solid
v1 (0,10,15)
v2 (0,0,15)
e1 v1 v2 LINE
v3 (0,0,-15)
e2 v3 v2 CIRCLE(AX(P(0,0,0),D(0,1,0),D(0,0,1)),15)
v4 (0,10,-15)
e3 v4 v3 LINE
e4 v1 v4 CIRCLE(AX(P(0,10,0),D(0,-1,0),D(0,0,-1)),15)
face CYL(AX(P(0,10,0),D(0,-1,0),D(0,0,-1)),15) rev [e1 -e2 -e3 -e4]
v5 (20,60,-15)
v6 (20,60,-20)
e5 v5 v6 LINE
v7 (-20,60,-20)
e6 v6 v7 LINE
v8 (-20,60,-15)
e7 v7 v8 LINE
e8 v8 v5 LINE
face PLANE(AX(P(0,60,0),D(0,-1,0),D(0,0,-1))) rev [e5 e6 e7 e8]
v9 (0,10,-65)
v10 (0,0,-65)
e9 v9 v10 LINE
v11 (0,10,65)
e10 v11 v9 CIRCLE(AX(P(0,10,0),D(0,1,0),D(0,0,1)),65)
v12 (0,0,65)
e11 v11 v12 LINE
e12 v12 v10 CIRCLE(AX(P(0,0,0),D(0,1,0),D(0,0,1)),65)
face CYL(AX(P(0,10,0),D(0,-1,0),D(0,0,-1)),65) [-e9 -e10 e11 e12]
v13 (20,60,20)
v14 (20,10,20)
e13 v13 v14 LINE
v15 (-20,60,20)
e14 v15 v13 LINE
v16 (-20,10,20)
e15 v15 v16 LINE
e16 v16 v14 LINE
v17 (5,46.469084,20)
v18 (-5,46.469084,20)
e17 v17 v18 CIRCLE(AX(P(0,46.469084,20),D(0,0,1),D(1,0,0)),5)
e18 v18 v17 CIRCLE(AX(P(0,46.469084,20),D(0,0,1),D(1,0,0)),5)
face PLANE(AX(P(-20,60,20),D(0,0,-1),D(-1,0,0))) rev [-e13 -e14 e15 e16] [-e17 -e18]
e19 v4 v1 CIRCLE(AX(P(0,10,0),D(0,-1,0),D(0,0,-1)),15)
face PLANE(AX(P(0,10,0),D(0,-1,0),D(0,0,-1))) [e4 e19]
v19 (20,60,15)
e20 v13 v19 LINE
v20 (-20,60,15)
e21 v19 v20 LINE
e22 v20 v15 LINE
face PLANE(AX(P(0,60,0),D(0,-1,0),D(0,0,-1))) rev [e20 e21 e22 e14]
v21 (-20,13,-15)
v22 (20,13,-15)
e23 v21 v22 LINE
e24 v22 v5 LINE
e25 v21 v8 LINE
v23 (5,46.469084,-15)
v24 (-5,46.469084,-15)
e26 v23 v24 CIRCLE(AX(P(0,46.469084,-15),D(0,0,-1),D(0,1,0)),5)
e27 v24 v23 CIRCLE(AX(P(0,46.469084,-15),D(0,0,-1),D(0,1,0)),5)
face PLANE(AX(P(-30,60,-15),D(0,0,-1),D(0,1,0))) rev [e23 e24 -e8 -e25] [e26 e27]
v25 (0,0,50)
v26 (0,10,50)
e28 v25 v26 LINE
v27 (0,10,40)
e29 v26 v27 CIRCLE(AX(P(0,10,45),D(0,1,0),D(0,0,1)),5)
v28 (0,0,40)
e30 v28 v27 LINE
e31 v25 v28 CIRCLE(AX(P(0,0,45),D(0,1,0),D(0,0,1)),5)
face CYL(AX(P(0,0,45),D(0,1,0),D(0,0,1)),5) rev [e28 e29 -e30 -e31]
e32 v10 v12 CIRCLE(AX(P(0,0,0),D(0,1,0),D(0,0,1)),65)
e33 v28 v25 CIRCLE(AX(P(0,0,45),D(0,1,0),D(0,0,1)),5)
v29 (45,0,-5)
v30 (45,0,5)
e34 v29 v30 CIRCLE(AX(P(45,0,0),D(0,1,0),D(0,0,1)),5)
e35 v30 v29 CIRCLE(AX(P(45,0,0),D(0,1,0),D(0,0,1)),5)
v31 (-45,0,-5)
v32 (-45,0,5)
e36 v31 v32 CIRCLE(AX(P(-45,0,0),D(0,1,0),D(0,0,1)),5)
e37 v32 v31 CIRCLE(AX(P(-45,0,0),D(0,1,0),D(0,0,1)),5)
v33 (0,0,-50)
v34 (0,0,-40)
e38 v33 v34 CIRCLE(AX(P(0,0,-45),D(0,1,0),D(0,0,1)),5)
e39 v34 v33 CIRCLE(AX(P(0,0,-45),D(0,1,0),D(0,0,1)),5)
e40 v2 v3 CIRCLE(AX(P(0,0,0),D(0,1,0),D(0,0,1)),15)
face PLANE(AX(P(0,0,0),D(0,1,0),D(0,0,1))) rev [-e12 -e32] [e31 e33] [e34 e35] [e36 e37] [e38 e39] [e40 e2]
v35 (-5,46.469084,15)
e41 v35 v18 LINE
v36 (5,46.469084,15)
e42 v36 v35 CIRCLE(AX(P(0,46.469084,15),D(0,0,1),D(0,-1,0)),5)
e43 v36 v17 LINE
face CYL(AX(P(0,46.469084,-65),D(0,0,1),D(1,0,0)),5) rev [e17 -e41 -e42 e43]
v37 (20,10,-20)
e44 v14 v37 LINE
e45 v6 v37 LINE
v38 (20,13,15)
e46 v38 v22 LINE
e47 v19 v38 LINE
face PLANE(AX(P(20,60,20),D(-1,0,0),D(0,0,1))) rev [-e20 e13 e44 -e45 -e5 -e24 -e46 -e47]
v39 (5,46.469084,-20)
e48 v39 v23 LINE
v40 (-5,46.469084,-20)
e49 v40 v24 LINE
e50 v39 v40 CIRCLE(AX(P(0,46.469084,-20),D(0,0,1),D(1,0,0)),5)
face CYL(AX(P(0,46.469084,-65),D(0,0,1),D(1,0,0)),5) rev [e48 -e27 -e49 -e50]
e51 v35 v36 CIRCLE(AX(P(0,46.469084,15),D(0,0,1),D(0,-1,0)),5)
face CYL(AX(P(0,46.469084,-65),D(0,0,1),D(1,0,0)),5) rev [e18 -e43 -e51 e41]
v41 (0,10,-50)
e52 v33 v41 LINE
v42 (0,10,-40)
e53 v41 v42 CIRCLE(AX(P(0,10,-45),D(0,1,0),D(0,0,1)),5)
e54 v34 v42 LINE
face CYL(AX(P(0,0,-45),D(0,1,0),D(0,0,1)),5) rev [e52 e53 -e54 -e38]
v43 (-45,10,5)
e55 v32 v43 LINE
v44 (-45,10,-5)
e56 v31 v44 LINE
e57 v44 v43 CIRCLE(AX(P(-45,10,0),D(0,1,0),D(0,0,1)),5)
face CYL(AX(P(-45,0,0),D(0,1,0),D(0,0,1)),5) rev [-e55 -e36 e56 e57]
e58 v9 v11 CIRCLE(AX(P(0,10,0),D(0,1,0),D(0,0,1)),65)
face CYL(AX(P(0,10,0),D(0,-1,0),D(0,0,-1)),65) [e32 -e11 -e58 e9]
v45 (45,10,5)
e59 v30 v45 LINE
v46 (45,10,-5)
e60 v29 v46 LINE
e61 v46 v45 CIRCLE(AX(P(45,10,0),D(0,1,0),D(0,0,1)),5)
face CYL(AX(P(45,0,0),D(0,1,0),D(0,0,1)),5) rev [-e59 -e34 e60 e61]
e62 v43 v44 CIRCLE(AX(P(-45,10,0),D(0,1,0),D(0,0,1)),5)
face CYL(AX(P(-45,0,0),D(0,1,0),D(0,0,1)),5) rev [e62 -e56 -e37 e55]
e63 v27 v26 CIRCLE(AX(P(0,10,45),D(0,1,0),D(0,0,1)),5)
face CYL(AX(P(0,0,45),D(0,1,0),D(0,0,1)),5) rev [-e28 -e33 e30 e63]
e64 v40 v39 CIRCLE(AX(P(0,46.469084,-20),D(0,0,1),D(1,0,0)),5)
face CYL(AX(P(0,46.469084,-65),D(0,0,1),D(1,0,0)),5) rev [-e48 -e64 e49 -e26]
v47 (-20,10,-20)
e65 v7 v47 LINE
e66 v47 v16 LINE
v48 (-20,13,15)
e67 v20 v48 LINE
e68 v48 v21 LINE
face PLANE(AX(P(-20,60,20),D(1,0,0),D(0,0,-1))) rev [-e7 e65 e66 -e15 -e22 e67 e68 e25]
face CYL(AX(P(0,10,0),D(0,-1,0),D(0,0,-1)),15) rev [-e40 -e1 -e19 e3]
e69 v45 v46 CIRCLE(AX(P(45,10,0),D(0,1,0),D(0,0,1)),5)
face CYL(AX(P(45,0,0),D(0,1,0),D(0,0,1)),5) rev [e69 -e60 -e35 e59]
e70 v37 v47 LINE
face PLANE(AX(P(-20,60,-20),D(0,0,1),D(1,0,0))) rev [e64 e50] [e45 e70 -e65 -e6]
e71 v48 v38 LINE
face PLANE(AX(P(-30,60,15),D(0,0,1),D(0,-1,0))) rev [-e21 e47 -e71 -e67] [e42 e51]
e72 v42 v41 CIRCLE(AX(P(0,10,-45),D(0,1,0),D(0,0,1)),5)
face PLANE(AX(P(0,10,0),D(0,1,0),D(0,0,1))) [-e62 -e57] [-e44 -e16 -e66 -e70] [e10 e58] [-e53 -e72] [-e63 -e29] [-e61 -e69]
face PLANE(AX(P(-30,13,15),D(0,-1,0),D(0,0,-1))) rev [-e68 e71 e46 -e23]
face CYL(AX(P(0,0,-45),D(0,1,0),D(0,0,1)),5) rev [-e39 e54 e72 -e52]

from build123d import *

# Parameters (mm, degrees)
SKETCH1_R           = 65
SKETCH1_R_2         = 15
BOSS_EXTRUDE1_DEPTH = 10
SKETCH2_R           = 5
CUT_EXTRUDE1_DEPTH  = 10
SKETCH3_W           = 40
SKETCH3_H           = 40
BOSS_EXTRUDE2_DEPTH = 50
SKETCH4_W           = 30
SKETCH4_H           = 47
CUT_EXTRUDE2_DEPTH  = 50
SKETCH5_R           = 5
CUT_EXTRUDE3_DEPTH  = 123.678441464


with BuildPart() as part:
    # Sketch1 → Boss-Extrude1 (new body)
    with BuildSketch(Plane(origin=(0, 0, 0), x_dir=(1, 0, 0), z_dir=(0, 1, 0))):
        with Locations(Location((0, 0, 0), (0, 0, 270))):
            Circle(SKETCH1_R)
        with Locations(Location((0, 0, 0), (0, 0, 270))):
            Circle(SKETCH1_R_2, mode=Mode.SUBTRACT)
    extrude(amount=BOSS_EXTRUDE1_DEPTH)

    # Sketch2 → Cut-Extrude1 (cut)
    with BuildSketch(Plane(origin=(0, 10, 0), x_dir=(1, 0, 0), z_dir=(0, 1, 0))):
        with Locations(Location((0, 45, 0), (0, 0, 270))):
            Circle(SKETCH2_R)
        with Locations(Location((45, 0, 0), (0, 0, 270))):
            Circle(SKETCH2_R)
        with Locations(Location((0, -45, 0), (0, 0, 270))):
            Circle(SKETCH2_R)
        with Locations(Location((-45, 0, 0), (0, 0, 270))):
            Circle(SKETCH2_R)
    extrude(amount=-CUT_EXTRUDE1_DEPTH, mode=Mode.SUBTRACT)

    # Sketch3 → Boss-Extrude2 (add)
    with BuildSketch(Plane(origin=(0, 10, 0), x_dir=(1, 0, 0), z_dir=(0, 1, 0))):
        Rectangle(SKETCH3_W, SKETCH3_H)
    extrude(amount=BOSS_EXTRUDE2_DEPTH)

    # Sketch4 → Cut-Extrude2 (cut)
    with BuildSketch(Plane(origin=(20, 0, 0), x_dir=(0, 0, -1), z_dir=(1, 0, 0))):
        with Locations((0, 36.5)):
            Rectangle(SKETCH4_W, SKETCH4_H)
    extrude(amount=-CUT_EXTRUDE2_DEPTH, mode=Mode.SUBTRACT)

    # Sketch5 → Cut-Extrude3 (cut, through all)
    with BuildSketch(Plane.XY.offset(20)):
        with Locations((0, 46.469084147)):
            Circle(SKETCH5_R)
    extrude(amount=-CUT_EXTRUDE3_DEPTH, mode=Mode.SUBTRACT)


solid = part.part
